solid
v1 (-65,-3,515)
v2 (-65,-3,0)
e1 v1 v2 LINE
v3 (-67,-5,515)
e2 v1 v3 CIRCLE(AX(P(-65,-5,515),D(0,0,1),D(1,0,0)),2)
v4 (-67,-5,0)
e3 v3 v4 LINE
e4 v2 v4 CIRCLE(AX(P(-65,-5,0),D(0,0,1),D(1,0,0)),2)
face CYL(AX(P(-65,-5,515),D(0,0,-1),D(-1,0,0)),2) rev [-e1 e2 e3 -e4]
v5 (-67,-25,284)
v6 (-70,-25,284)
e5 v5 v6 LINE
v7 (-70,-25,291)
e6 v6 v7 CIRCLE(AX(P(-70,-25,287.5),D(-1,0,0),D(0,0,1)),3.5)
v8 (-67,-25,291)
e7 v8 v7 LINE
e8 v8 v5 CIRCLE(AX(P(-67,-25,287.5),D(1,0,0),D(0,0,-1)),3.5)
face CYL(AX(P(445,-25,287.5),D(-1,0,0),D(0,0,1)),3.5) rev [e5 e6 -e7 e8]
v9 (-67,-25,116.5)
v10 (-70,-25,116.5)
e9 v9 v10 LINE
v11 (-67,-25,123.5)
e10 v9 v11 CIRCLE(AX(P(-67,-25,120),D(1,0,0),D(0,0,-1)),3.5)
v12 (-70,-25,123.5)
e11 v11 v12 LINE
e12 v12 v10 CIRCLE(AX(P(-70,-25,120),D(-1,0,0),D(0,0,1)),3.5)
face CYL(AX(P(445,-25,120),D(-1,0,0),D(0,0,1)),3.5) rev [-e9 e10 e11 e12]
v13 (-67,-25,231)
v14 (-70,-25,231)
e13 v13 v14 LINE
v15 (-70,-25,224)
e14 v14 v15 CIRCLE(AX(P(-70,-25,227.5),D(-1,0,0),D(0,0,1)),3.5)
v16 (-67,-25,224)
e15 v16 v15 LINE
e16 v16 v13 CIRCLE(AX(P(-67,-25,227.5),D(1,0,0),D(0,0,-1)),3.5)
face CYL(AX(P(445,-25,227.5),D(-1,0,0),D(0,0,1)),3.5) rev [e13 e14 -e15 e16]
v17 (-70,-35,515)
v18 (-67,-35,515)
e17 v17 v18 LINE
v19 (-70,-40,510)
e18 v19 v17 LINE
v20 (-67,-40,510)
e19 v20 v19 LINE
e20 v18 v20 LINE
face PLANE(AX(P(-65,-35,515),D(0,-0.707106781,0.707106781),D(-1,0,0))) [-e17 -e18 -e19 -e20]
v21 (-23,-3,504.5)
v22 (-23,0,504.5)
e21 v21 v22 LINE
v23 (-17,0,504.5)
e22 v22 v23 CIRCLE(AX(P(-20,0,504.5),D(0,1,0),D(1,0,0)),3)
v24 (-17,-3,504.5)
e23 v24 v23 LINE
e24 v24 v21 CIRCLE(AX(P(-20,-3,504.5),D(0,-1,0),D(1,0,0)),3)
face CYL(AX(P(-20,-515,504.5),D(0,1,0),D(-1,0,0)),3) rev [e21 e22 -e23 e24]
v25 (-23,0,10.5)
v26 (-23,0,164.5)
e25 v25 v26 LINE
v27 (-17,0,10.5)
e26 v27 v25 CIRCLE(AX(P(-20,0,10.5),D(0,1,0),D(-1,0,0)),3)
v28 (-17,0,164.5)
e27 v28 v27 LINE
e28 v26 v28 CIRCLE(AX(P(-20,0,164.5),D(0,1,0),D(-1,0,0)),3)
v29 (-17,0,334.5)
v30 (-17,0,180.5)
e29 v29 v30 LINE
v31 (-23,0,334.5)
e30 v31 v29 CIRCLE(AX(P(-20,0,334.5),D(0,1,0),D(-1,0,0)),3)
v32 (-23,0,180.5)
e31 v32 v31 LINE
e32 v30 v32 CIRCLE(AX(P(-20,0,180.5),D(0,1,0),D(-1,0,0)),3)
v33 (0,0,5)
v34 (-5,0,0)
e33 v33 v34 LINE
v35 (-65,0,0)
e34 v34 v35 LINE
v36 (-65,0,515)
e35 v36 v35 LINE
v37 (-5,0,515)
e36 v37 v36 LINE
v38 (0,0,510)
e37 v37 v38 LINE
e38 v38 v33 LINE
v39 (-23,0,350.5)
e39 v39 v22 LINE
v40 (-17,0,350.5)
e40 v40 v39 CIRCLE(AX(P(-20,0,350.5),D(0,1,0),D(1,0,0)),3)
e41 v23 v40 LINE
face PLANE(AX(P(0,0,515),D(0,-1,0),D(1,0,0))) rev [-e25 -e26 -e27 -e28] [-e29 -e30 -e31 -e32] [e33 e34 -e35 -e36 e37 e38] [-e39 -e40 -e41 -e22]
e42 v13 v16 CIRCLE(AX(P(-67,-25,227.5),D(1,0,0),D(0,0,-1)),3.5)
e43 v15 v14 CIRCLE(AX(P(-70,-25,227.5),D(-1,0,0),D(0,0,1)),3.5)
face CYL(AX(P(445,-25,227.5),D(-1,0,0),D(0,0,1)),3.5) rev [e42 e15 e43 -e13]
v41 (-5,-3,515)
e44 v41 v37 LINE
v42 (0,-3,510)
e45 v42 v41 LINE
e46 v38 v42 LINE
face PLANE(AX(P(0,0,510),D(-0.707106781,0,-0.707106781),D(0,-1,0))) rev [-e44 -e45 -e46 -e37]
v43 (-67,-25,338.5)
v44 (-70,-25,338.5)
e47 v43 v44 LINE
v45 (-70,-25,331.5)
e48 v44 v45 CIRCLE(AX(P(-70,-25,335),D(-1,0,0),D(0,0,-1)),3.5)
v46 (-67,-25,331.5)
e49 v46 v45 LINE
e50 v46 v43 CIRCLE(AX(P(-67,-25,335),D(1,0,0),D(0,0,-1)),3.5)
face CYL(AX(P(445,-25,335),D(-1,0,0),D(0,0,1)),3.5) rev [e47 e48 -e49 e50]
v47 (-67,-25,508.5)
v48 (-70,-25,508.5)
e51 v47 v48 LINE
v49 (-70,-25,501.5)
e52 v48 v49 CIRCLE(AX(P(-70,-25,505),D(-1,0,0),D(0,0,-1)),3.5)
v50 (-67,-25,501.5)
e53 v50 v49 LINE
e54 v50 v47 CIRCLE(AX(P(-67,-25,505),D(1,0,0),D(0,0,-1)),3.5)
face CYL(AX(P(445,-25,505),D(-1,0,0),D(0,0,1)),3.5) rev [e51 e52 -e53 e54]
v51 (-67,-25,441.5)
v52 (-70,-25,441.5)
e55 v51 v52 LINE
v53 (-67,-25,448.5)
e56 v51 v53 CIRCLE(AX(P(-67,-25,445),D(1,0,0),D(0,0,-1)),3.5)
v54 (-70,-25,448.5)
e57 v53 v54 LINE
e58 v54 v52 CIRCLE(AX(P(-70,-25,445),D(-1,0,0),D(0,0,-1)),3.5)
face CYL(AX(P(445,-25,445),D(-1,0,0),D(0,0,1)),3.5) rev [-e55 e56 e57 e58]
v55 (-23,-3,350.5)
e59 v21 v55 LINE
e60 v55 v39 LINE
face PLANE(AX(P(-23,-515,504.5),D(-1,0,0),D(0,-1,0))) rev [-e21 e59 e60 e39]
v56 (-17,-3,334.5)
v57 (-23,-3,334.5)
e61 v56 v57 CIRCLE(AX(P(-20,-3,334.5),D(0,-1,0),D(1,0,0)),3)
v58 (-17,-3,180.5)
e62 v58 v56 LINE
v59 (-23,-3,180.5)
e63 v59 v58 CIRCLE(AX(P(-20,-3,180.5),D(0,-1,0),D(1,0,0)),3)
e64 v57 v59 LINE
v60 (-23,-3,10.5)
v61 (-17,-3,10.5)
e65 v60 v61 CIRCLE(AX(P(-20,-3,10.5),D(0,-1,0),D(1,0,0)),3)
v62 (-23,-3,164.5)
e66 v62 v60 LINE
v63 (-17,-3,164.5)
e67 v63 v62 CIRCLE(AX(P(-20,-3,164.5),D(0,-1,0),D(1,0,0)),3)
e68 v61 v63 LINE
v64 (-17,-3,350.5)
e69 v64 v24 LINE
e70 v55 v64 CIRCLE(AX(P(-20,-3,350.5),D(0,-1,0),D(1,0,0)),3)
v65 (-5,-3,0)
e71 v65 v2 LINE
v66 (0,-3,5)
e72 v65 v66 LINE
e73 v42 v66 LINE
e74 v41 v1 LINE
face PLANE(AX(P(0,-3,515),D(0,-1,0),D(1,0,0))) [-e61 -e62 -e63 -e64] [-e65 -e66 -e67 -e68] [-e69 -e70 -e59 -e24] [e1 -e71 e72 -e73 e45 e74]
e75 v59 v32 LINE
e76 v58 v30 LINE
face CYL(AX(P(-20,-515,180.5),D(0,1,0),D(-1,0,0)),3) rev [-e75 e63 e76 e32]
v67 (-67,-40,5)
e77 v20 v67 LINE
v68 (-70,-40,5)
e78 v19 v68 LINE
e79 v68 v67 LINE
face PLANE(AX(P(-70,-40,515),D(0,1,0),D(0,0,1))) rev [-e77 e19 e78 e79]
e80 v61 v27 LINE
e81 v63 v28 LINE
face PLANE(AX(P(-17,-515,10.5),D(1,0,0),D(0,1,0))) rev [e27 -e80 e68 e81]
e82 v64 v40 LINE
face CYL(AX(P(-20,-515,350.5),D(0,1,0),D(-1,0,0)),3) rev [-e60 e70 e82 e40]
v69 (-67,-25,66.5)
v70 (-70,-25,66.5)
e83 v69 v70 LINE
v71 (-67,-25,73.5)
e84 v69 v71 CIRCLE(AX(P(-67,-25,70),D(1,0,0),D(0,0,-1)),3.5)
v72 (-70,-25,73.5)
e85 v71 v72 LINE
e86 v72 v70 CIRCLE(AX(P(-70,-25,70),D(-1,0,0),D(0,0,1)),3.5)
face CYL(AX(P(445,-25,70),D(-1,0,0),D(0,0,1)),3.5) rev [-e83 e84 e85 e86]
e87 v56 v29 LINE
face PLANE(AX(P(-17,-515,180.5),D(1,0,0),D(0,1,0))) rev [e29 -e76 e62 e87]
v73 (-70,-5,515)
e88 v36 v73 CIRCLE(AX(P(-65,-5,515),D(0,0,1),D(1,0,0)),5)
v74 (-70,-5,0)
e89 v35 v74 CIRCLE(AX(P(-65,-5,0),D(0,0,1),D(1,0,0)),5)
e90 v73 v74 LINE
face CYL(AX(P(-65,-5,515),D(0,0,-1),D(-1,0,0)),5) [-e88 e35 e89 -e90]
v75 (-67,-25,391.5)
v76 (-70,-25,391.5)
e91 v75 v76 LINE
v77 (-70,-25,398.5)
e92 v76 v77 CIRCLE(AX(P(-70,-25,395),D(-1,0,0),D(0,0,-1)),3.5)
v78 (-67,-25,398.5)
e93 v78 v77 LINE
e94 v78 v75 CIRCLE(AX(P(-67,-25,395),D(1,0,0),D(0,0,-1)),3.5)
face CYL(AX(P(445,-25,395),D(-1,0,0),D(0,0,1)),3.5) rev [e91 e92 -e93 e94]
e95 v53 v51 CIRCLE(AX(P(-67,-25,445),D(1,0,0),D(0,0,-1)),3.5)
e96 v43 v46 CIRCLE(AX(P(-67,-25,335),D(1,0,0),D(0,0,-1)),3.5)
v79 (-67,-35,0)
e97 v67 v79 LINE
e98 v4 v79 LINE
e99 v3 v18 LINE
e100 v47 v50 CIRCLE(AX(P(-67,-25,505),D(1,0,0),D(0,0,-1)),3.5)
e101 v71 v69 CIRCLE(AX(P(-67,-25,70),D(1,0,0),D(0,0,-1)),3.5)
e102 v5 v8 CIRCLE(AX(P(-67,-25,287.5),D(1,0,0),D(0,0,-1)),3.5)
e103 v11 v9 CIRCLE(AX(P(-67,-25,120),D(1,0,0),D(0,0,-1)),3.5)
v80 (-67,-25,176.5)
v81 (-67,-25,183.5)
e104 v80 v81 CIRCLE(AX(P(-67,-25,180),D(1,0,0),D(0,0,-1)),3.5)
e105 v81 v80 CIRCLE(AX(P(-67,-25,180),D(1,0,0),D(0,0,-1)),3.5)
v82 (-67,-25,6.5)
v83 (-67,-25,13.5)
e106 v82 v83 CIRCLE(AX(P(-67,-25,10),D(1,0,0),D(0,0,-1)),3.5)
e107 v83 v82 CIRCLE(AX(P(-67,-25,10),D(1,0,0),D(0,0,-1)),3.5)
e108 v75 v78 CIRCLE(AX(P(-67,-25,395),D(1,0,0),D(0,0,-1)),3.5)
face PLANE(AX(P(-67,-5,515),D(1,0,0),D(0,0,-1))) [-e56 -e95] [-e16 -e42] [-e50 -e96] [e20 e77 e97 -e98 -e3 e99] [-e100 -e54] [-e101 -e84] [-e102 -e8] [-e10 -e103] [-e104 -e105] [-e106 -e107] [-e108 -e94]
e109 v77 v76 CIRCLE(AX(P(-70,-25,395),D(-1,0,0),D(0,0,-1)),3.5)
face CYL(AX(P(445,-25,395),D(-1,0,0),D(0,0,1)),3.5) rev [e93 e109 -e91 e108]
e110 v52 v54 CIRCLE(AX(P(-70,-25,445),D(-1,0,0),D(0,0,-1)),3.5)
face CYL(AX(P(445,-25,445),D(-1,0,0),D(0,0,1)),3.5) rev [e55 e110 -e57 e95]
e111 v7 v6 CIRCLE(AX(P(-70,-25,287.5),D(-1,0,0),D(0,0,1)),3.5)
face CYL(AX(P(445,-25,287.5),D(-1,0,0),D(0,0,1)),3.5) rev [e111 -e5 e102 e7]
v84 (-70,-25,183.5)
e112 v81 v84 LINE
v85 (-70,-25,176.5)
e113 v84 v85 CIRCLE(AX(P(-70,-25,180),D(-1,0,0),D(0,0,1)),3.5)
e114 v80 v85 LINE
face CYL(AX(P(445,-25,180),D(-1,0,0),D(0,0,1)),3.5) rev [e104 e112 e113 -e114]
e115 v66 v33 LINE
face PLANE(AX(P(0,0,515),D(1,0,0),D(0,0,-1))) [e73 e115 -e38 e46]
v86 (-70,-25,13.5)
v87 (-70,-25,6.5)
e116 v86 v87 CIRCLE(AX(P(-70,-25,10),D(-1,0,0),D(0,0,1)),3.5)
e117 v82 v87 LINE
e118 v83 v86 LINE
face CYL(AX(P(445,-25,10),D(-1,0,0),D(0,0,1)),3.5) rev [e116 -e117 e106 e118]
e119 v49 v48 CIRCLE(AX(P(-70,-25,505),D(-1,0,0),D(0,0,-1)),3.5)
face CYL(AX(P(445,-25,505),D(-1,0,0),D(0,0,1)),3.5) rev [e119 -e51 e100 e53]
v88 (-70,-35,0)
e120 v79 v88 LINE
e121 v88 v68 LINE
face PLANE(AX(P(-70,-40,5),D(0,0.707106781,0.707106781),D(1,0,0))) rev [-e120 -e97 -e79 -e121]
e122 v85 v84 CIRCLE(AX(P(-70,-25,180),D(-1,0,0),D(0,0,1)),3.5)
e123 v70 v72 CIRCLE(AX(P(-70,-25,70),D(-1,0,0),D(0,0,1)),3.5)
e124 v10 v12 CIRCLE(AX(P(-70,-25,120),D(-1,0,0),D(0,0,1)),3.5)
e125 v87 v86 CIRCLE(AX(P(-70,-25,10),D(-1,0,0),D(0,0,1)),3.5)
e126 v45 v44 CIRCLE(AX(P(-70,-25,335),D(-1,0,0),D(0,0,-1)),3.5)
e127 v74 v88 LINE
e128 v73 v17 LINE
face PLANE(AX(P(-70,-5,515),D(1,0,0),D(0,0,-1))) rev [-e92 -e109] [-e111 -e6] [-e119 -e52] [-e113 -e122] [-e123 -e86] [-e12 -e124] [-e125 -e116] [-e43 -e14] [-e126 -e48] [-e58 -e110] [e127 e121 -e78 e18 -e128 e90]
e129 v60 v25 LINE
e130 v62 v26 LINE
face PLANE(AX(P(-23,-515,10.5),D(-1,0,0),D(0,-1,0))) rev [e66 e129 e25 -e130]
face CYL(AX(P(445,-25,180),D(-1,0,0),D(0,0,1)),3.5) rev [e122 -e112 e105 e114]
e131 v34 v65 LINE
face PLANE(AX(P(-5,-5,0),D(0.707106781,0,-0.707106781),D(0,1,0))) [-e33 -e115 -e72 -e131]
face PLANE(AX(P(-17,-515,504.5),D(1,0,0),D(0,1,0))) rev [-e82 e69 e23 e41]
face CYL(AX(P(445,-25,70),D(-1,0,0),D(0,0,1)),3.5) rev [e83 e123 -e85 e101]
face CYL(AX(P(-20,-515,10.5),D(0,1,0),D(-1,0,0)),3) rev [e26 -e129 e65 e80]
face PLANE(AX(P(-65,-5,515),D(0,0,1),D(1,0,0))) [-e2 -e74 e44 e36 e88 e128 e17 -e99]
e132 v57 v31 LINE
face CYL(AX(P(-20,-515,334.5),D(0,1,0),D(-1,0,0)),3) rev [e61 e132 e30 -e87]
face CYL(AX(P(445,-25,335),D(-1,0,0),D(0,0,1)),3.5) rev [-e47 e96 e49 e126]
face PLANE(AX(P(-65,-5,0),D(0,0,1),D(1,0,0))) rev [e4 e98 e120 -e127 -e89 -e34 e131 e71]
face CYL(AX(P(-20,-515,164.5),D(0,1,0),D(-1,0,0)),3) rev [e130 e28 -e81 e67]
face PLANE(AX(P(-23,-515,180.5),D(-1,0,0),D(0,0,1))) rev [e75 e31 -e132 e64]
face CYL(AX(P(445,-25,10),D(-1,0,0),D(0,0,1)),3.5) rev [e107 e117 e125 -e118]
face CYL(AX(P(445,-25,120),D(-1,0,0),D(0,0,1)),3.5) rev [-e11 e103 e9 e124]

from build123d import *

# Parameters (mm, degrees)
EXTRUDE_1_DEPTH     = 515
SKETCH_3_R          = 3.5
CUT_EXTRUDE_1_DEPTH = 515
CHAMFER_1_SIZE      = 5
CUT_EXTRUDE_2_DEPTH = 515


with BuildPart() as part:
    # 草图1 → 凸台-拉伸1 (new body)
    with BuildSketch(Plane.XY):
        with BuildLine():
            Line((0, 0), (-65, 0))
            ThreePointArc((-65, 0), (-68.535533906, -1.464466094), (-70, -5))
            Line((-70, -5), (-70, -40))
            Line((-70, -40), (-67, -40))
            Line((-67, -40), (-67, -5))
            ThreePointArc((-67, -5), (-66.414213562, -3.585786438), (-65, -3))
            Line((-65, -3), (0, -3))
            Line((0, -3), (0, 0))
        make_face()
    extrude(amount=EXTRUDE_1_DEPTH)

    # 草图3 → 切除-拉伸1 (cut)
    with BuildSketch(Plane.ZY.offset(70)):
        with Locations((10, -25)):
            Circle(SKETCH_3_R)
        with Locations((70, -25)):
            Circle(SKETCH_3_R)
        with Locations((287.5, -25)):
            Circle(SKETCH_3_R)
        with Locations((180, -25)):
            Circle(SKETCH_3_R)
        with Locations((120, -25)):
            Circle(SKETCH_3_R)
        with Locations((227.5, -25)):
            Circle(SKETCH_3_R)
        with Locations(Location((445, -25, 0), (0, 0, 180))):
            Circle(SKETCH_3_R)
        with Locations(Location((505, -25, 0), (0, 0, 180))):
            Circle(SKETCH_3_R)
        with Locations(Location((395, -25, 0), (0, 0, 180))):
            Circle(SKETCH_3_R)
        with Locations(Location((335, -25, 0), (0, 0, 180))):
            Circle(SKETCH_3_R)
    extrude(amount=-CUT_EXTRUDE_1_DEPTH, mode=Mode.SUBTRACT)

    # 倒角1
    chamfer_1_edges = [part.edges().sort_by_distance(p)[0] for p in [
        (-68.5, -40, 0),
        (0, -1.5, 515),
        (-68.5, -40, 515),
        (0, -1.5, 0),
    ]]
    chamfer(chamfer_1_edges, length=CHAMFER_1_SIZE)

    # 草图4 → 切除-拉伸2 (cut)
    with BuildSketch(Plane(origin=(0, 0, 0), x_dir=(1, 0, 0), z_dir=(0, 1, 0))):
        with BuildLine():
            Line((-17, -10.5), (-17, -164.5))
            ThreePointArc((-17, -164.5), (-20, -167.5), (-23, -164.5))
            Line((-23, -164.5), (-23, -10.5))
            ThreePointArc((-23, -10.5), (-20, -7.5), (-17, -10.5))
        make_face()
        with BuildLine():
            Line((-17, -180.5), (-17, -334.5))
            ThreePointArc((-17, -334.5), (-20, -337.5), (-23, -334.5))
            Line((-23, -334.5), (-23, -180.5))
            ThreePointArc((-23, -180.5), (-20, -177.5), (-17, -180.5))
        make_face()
        with BuildLine():
            Line((-17, -504.5), (-17, -350.5))
            ThreePointArc((-17, -350.5), (-20, -347.5), (-23, -350.5))
            Line((-23, -350.5), (-23, -504.5))
            ThreePointArc((-23, -504.5), (-20, -507.5), (-17, -504.5))
        make_face()
    extrude(amount=-CUT_EXTRUDE_2_DEPTH, mode=Mode.SUBTRACT)


solid = part.part
